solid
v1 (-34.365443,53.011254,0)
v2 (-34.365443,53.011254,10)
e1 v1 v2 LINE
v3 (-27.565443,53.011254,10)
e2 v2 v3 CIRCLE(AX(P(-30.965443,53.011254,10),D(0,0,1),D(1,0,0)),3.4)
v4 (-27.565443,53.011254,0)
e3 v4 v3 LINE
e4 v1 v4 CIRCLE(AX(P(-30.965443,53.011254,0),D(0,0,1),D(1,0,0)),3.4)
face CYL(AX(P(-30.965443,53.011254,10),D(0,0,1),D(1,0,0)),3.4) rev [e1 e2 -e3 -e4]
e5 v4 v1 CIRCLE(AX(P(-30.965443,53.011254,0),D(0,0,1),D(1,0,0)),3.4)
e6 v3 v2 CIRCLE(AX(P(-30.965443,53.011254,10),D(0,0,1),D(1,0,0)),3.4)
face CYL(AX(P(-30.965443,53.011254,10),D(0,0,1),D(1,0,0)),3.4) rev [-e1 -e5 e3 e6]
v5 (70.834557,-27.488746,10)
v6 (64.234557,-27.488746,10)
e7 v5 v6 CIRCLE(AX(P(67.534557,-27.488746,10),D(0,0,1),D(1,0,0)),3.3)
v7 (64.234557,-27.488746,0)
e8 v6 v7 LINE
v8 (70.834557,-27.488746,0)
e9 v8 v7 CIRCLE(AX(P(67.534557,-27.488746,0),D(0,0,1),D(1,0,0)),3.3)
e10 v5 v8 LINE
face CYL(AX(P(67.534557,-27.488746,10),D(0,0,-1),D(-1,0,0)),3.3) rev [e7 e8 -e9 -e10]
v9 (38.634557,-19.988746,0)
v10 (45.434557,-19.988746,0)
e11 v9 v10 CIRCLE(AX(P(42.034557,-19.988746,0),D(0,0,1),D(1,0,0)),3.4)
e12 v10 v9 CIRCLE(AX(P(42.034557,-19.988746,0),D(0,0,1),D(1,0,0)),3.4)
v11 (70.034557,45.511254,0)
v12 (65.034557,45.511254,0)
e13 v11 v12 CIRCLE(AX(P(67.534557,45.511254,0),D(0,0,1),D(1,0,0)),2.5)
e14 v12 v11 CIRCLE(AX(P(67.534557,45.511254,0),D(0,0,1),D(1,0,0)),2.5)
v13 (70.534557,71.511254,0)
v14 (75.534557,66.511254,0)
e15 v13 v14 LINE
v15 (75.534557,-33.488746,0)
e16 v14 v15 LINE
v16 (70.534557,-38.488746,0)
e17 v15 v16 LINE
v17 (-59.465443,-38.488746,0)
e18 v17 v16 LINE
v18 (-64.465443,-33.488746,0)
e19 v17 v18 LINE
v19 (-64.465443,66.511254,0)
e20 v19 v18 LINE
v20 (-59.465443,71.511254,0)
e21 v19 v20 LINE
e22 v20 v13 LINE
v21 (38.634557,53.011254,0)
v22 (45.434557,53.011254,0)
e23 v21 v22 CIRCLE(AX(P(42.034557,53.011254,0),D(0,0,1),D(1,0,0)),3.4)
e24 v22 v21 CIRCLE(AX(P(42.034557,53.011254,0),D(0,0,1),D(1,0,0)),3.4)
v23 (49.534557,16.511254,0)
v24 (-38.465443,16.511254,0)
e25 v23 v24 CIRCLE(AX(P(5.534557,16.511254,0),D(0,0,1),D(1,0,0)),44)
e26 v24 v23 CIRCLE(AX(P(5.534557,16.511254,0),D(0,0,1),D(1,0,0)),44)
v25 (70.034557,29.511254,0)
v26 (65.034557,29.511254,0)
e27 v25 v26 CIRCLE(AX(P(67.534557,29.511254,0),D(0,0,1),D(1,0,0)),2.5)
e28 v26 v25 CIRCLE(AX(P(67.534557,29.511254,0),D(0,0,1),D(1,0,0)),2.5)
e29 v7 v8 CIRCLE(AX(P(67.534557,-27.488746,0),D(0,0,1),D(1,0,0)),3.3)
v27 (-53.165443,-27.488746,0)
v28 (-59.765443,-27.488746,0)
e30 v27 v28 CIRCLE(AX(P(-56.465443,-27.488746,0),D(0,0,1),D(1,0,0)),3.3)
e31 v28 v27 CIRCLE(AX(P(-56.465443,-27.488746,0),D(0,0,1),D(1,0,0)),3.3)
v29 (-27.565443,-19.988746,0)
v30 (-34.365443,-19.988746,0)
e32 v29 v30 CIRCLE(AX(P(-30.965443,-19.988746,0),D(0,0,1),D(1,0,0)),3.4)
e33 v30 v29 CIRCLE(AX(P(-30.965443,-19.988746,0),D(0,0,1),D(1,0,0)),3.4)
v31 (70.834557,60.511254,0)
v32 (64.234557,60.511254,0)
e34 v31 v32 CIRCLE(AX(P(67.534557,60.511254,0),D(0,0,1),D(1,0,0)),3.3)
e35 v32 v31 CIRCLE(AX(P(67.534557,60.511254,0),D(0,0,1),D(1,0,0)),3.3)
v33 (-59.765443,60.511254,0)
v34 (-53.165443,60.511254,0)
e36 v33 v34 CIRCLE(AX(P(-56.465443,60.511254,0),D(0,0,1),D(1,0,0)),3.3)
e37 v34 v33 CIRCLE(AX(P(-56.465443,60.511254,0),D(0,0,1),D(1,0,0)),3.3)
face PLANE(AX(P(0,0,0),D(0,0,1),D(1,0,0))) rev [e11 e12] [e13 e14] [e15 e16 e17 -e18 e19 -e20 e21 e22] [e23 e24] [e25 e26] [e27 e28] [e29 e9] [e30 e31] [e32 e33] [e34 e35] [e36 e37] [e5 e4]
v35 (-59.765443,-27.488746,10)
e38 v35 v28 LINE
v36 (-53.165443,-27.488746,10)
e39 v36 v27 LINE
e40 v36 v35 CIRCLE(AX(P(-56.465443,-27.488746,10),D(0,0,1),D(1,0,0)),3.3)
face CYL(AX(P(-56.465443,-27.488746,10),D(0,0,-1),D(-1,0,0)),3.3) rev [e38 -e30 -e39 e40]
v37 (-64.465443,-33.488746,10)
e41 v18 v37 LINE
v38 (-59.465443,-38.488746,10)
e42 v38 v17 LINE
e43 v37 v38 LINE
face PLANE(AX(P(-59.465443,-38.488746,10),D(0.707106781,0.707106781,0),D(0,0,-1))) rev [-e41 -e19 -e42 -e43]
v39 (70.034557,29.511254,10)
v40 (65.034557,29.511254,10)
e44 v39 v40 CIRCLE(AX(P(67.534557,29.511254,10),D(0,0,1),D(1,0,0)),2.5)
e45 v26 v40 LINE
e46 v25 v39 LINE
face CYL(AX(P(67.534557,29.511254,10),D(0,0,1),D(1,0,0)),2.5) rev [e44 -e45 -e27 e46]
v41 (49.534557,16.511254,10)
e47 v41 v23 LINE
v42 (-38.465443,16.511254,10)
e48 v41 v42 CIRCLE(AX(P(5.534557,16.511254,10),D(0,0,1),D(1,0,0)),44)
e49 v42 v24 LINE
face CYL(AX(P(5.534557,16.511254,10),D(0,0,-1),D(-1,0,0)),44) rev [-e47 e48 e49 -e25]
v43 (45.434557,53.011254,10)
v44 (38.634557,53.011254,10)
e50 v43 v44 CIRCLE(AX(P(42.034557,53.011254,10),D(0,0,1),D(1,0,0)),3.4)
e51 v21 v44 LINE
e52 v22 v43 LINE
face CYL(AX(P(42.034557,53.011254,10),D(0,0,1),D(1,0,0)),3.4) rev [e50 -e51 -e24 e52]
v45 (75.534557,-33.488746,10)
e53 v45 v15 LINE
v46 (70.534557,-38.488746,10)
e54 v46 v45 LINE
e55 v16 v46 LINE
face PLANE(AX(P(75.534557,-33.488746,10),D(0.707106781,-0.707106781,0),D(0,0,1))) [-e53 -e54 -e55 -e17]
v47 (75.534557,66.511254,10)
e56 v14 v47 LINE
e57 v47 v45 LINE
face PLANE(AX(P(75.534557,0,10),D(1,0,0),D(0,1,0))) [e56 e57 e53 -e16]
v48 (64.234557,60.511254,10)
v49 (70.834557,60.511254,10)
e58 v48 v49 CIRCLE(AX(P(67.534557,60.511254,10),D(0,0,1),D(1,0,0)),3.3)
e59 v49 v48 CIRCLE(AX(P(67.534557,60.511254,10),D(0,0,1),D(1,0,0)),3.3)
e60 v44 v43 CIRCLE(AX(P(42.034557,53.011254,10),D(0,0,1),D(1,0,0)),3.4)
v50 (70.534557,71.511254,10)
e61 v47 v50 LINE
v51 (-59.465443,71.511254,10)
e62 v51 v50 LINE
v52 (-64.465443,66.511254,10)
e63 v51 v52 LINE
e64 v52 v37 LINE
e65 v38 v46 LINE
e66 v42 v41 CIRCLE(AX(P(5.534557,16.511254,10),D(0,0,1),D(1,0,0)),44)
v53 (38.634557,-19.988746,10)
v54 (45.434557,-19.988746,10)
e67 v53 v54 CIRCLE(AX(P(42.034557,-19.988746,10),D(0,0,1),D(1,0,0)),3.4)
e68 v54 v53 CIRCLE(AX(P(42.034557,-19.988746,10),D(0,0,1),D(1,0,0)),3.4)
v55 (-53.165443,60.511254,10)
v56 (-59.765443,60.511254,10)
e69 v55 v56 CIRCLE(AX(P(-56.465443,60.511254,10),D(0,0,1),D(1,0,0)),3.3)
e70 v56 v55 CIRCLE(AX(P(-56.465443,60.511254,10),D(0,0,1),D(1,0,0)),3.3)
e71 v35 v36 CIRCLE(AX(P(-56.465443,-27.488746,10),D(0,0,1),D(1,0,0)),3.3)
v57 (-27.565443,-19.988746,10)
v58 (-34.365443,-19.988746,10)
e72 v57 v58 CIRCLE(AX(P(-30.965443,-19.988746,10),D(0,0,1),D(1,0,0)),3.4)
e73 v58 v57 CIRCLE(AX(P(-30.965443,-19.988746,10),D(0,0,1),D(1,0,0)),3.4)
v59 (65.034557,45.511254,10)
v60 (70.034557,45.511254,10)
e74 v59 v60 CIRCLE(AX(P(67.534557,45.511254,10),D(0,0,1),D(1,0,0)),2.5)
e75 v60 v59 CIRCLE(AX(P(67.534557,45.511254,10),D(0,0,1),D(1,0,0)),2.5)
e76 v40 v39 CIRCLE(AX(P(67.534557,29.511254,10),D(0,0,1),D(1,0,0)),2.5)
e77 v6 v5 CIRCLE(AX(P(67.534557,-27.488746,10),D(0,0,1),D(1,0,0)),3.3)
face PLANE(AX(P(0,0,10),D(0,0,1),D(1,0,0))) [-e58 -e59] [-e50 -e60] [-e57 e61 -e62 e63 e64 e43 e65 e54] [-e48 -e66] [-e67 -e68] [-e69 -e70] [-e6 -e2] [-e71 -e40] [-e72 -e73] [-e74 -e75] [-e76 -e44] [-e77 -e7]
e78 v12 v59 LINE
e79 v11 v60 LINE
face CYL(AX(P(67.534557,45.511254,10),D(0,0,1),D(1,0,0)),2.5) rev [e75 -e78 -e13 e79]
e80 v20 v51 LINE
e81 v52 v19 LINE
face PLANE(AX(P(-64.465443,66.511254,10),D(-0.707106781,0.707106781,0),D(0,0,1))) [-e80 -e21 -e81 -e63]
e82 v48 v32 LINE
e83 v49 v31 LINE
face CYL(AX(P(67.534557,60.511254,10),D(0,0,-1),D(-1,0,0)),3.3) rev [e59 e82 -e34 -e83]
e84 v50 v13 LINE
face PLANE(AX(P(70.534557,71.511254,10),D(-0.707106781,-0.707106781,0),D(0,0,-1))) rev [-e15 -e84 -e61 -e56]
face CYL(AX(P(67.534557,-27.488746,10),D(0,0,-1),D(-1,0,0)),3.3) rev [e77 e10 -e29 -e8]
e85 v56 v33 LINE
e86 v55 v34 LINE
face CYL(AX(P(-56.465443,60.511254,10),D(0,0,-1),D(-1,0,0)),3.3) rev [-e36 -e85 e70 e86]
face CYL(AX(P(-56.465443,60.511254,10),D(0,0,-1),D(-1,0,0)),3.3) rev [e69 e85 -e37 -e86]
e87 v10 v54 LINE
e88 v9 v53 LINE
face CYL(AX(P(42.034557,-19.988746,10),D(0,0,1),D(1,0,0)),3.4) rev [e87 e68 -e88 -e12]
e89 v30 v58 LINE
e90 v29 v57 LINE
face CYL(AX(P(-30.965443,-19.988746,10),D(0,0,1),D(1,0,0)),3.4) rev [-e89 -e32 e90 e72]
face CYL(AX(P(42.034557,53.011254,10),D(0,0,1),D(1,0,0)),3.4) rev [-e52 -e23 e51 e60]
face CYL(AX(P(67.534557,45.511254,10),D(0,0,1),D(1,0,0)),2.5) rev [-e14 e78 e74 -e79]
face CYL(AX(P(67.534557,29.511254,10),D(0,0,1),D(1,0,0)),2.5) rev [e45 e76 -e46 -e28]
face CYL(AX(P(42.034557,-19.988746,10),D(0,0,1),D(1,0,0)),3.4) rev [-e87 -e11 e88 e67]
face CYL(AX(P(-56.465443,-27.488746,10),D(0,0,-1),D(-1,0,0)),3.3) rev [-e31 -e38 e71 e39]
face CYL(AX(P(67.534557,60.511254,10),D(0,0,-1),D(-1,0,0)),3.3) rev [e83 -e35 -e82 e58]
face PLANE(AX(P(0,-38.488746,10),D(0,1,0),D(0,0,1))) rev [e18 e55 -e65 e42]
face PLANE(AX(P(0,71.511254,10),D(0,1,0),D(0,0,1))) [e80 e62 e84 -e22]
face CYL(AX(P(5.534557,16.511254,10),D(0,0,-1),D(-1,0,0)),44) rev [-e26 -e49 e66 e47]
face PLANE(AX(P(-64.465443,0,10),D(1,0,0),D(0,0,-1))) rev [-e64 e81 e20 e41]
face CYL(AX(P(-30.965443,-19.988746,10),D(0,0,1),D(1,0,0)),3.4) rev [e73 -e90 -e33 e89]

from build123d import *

# Parameters (mm, degrees)
SKETCH1_W           = 140
SKETCH1_H           = 110
SKETCH1_R           = 3.3
SKETCH1_R_2         = 44
BOSS_EXTRUDE1_DEPTH = 10
M8_TAPPED_HOLE1_D   = 6.8
CHAMFER1_SIZE       = 5
M6_TAPPED_HOLE1_D   = 5


with BuildPart() as part:
    # Sketch1 → Boss-Extrude1 (new body)
    with BuildSketch(Plane.XY):
        with Locations((5.534557186, 16.511254019)):
            Rectangle(SKETCH1_W, SKETCH1_H)
        with Locations((67.534557186, 60.511254019)):
            Circle(SKETCH1_R, mode=Mode.SUBTRACT)
        with Locations((67.534557186, -27.488745981)):
            Circle(SKETCH1_R, mode=Mode.SUBTRACT)
        with Locations((-56.465442814, -27.488745981)):
            Circle(SKETCH1_R, mode=Mode.SUBTRACT)
        with Locations((-56.465442814, 60.511254019)):
            Circle(SKETCH1_R, mode=Mode.SUBTRACT)
        with Locations((5.534557186, 16.511254019)):
            Circle(SKETCH1_R_2, mode=Mode.SUBTRACT)
    extrude(amount=BOSS_EXTRUDE1_DEPTH)

    # M8 Tapped Hole1 (through all)
    with Locations(Plane.XY.offset(10)):
        with Locations((-30.965442814, 53.011254019), (42.034557186, 53.011254019), (42.034557186, -19.988745981), (-30.965442814, -19.988745981)):
            Hole(M8_TAPPED_HOLE1_D / 2)

    # Chamfer1
    chamfer1_edges = [part.edges().sort_by_distance(p)[0] for p in [
        (75.534557186, -38.488745981, 5),
        (-64.465442814, -38.488745981, 5),
        (-64.465442814, 71.511254019, 5),
        (75.534557186, 71.511254019, 5),
    ]]
    chamfer(chamfer1_edges, length=CHAMFER1_SIZE)

    # M6 Tapped Hole1 (through all)
    with Locations(Plane.XY.offset(10)):
        with Locations((67.534557186, 45.511254019), (67.534557186, 29.511254019)):
            Hole(M6_TAPPED_HOLE1_D / 2)


solid = part.part
